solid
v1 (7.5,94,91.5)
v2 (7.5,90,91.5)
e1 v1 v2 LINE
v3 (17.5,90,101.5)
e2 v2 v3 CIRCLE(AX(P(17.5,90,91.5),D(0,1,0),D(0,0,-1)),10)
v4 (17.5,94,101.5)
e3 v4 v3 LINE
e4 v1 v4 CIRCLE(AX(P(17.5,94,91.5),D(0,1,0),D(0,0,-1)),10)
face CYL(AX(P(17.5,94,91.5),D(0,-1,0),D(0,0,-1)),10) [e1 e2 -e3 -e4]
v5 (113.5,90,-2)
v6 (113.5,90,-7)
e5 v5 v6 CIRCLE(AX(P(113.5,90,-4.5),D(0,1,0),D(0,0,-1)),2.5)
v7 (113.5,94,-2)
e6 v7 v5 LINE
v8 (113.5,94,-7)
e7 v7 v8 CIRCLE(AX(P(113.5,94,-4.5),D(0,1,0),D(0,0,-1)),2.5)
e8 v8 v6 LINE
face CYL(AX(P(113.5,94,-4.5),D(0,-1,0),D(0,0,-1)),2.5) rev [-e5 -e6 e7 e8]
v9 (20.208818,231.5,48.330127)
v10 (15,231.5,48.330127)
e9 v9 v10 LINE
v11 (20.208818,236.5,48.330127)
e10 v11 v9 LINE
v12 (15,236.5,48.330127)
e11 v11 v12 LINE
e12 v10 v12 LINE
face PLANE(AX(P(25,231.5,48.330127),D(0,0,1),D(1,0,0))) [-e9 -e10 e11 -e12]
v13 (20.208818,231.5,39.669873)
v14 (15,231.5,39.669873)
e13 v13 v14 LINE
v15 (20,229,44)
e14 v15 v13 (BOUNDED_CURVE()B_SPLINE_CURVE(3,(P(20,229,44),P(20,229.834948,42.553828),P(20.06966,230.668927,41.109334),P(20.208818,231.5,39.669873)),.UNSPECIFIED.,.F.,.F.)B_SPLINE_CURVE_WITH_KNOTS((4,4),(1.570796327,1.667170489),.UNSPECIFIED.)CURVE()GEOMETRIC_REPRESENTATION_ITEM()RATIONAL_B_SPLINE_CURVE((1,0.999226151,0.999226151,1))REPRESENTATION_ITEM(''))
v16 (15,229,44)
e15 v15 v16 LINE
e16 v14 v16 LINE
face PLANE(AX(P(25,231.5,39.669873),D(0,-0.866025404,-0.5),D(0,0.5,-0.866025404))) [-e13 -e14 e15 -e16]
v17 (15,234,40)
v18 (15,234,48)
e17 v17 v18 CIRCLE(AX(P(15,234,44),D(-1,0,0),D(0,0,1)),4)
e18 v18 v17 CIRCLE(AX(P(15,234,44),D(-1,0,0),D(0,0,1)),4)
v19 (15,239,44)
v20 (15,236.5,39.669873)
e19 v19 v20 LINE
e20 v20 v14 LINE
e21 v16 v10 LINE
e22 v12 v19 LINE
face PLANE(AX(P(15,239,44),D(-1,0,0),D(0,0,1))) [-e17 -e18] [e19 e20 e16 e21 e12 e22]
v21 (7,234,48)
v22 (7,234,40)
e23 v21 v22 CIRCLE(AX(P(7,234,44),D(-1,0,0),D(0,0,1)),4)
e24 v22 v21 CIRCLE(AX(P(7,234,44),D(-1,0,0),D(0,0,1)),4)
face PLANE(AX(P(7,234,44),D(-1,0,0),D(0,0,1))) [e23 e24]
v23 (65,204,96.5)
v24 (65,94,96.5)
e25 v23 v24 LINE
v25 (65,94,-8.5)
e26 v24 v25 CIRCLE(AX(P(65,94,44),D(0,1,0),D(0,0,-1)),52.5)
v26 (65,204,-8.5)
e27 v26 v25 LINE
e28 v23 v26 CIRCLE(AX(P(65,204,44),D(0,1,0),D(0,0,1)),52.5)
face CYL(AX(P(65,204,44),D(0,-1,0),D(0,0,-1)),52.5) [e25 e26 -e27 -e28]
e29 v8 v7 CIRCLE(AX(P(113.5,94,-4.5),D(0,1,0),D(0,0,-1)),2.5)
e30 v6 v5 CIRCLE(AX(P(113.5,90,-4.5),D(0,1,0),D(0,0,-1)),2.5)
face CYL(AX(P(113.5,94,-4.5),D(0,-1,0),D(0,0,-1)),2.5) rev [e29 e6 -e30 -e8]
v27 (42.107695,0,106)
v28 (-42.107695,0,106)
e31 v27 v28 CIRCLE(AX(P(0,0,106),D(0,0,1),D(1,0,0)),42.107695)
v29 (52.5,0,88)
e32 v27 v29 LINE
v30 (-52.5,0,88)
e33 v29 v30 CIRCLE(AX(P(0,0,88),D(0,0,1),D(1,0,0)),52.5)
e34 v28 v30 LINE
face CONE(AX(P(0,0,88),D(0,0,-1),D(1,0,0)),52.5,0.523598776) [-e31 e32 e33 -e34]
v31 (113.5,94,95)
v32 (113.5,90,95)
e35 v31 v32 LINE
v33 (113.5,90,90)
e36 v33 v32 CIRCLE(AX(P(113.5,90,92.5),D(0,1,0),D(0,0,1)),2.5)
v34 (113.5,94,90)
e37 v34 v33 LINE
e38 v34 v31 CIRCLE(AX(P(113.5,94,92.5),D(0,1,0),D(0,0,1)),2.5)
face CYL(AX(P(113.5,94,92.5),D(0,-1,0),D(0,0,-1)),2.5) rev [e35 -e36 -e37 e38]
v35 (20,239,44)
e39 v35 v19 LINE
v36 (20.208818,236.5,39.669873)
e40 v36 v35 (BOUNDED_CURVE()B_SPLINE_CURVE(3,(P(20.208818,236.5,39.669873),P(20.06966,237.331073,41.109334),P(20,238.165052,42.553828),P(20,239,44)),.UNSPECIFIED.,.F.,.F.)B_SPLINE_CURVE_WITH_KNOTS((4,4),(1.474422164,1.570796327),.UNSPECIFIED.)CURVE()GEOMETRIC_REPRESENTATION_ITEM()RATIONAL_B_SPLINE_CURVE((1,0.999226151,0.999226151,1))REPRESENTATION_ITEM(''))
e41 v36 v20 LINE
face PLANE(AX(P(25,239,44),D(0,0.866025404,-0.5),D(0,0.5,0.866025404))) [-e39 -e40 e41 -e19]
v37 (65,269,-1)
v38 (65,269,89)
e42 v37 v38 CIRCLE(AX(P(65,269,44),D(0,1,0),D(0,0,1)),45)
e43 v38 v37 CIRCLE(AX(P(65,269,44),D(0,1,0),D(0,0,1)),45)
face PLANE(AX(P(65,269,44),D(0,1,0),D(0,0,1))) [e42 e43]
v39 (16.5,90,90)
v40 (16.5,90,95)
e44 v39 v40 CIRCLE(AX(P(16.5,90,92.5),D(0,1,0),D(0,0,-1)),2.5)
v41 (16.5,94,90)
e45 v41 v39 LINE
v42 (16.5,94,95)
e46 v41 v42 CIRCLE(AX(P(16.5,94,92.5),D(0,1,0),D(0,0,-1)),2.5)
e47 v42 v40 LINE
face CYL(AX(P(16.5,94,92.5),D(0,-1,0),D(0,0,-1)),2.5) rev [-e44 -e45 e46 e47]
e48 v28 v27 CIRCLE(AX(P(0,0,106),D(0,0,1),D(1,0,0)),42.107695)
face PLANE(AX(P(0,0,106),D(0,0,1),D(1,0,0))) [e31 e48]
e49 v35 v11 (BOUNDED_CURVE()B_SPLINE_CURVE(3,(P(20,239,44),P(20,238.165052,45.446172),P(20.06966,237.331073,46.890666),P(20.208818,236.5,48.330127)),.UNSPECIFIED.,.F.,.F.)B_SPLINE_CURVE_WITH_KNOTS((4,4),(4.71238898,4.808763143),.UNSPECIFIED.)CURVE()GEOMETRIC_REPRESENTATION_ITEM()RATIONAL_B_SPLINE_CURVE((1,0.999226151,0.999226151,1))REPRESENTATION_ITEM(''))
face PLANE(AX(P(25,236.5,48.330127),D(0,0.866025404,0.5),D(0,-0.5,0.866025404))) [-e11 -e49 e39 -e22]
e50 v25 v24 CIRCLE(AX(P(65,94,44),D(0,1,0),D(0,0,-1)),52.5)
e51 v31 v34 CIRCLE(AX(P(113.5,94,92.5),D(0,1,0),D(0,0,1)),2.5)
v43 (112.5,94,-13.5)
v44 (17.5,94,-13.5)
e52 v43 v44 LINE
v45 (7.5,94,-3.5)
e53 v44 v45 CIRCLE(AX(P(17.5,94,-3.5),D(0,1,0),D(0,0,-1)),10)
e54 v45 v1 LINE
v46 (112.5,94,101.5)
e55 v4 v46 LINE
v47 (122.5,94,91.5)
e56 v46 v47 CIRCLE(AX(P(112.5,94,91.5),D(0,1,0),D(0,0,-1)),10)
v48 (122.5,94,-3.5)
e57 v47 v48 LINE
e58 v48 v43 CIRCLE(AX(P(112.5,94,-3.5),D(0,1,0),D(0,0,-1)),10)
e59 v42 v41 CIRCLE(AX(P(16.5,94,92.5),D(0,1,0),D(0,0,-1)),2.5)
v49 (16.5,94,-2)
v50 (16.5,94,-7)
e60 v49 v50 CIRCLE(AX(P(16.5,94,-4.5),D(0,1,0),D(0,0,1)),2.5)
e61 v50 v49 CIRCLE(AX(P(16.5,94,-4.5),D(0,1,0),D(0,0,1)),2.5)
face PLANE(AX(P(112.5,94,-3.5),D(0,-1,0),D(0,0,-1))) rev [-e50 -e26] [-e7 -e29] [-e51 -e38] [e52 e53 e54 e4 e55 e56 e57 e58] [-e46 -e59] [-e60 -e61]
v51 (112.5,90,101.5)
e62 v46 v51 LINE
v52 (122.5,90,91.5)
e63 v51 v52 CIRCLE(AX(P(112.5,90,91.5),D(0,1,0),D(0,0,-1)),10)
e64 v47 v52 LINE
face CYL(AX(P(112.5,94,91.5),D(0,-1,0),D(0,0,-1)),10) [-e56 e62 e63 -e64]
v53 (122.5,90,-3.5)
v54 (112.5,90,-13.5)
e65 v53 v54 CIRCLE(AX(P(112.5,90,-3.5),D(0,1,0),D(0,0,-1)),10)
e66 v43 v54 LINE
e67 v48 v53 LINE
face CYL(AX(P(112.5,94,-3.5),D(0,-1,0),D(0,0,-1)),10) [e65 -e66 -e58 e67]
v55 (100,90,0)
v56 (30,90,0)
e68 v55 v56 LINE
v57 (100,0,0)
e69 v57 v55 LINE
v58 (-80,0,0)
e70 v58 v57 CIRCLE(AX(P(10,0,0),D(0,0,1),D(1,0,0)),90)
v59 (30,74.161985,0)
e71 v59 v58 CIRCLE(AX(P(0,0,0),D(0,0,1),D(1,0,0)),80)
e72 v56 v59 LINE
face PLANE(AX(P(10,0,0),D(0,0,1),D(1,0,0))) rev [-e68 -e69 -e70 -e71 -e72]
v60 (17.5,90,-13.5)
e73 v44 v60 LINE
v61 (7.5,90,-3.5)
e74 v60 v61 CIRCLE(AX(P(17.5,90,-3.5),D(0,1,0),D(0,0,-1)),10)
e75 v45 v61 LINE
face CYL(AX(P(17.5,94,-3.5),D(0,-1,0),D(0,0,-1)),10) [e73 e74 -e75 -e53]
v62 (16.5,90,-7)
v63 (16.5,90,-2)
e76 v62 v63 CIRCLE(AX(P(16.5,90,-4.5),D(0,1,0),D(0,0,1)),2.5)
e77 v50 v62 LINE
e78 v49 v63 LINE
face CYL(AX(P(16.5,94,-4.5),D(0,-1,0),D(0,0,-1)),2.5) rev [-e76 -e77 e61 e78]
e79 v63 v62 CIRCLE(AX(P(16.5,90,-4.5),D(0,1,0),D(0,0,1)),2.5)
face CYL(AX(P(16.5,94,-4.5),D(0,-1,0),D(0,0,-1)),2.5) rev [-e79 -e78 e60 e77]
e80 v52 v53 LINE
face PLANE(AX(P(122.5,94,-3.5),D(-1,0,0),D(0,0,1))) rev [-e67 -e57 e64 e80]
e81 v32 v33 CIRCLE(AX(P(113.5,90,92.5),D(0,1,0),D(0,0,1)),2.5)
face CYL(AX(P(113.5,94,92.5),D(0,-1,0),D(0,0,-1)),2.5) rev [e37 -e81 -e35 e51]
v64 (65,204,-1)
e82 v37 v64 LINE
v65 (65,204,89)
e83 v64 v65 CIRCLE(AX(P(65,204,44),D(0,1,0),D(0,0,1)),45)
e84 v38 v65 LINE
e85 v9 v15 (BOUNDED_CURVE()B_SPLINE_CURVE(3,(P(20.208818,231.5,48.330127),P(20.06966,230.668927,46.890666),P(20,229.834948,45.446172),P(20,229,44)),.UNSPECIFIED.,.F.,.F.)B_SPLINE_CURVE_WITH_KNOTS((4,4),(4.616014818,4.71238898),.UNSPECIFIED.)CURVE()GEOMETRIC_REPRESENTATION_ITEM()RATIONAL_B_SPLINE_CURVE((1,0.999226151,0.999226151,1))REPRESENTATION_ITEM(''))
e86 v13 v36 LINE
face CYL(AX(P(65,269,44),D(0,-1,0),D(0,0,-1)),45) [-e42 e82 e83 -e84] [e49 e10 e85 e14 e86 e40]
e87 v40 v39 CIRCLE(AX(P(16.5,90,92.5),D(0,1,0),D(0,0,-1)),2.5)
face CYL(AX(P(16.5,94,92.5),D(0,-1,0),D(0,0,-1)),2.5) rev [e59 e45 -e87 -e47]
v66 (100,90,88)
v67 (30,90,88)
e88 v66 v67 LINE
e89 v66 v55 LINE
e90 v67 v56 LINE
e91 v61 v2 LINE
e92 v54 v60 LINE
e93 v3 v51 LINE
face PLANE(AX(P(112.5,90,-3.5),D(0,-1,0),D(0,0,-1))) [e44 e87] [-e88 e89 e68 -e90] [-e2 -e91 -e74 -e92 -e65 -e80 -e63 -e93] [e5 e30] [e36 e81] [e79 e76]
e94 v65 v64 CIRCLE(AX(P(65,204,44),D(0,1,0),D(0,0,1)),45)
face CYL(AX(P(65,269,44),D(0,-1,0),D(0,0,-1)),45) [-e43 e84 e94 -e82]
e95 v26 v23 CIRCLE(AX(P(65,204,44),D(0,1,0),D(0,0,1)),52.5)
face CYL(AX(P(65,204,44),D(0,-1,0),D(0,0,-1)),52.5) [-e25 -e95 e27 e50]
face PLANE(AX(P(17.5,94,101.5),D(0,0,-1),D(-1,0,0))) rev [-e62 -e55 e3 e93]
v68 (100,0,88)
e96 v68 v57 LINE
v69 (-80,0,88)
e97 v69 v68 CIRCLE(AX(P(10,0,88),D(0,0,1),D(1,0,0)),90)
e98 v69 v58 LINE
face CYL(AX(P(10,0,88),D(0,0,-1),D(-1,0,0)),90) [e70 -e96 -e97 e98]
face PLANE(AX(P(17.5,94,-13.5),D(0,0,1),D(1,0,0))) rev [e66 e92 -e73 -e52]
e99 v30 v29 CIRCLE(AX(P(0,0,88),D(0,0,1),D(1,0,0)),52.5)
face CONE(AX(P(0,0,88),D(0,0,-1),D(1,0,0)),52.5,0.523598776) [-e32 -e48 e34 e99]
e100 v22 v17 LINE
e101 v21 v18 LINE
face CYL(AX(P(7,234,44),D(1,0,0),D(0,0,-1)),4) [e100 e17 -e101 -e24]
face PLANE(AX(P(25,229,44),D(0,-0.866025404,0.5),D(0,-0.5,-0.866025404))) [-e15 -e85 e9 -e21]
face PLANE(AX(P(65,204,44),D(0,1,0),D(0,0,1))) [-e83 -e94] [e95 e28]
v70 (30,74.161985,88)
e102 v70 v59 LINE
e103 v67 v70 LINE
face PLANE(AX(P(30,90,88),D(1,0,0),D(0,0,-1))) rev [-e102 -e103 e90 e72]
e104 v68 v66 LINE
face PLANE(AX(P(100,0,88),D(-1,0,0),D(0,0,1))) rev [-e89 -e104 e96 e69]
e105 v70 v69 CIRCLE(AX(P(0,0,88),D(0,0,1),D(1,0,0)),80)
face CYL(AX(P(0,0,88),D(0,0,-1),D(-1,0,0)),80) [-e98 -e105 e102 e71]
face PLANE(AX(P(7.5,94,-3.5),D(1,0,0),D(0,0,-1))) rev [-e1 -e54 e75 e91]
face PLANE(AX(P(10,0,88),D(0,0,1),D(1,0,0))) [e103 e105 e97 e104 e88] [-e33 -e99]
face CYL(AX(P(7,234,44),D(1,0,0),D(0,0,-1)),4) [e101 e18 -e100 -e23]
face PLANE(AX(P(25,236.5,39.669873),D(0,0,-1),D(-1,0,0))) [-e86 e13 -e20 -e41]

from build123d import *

# Parameters (mm, degrees)
EXTRUDE_1_DEPTH      = 88
SKETCH_2_R           = 52.5
EXTRUDE_2_DEPTH      = 18
EXTRUDE_2_TAPER      = 30
SKETCH_3_R           = 2.5
EXTRUDE_3_DEPTH      = 4
SKETCH_4_R           = 52.5
EXTRUDE_4_DEPTH      = 110
SKETCH_5_R           = 45
EXTRUDE_5_DEPTH      = 65
EXTRUDE_6_DEPTH      = 5
EXTRUDE_6_DEPTH_BACK = 5
SKETCH_7_R           = 4
EXTRUDE_7_DEPTH      = 8


with BuildPart() as part:
    # 草图1 → 凸台-拉伸1 (new body)
    with BuildSketch(Plane.XY):
        with BuildLine():
            Line((100, 0), (100, 90))
            Line((100, 90), (30, 90))
            Line((30, 90), (30, 74.161984871))
            ThreePointArc((30, 74.161984871), (-44.72135955, 66.332495807), (-80, 0))
            ThreePointArc((-80, 0), (10, -90), (100, 0))
        make_face()
    extrude(amount=EXTRUDE_1_DEPTH)

    # 草图2 → 凸台-拉伸2 (add)
    with BuildSketch(Plane.XY.offset(88)):
        Circle(SKETCH_2_R)
    extrude(amount=EXTRUDE_2_DEPTH, taper=EXTRUDE_2_TAPER)

    # 草图3 → 凸台-拉伸3 (add)
    with BuildSketch(Plane(origin=(0, 90, 0), x_dir=(1, 0, 0), z_dir=(0, 1, 0))):
        with BuildLine():
            Line((17.5, 13.5), (112.5, 13.5))
            ThreePointArc((112.5, 13.5), (119.571067812, 10.571067812), (122.5, 3.5))
            Line((122.5, 3.5), (122.5, -91.5))
            ThreePointArc((122.5, -91.5), (119.571067812, -98.571067812), (112.5, -101.5))
            Line((112.5, -101.5), (17.5, -101.5))
            ThreePointArc((17.5, -101.5), (10.428932188, -98.571067812), (7.5, -91.5))
            Line((7.5, -91.5), (7.5, 3.5))
            ThreePointArc((7.5, 3.5), (10.428932188, 10.571067812), (17.5, 13.5))
        make_face()
        with Locations(Location((16.5, 4.5, 0), (0, 0, 270))):
            Circle(SKETCH_3_R, mode=Mode.SUBTRACT)
        with Locations(Location((16.5, -92.5, 0), (0, 0, 90))):
            Circle(SKETCH_3_R, mode=Mode.SUBTRACT)
        with Locations(Location((113.5, -92.5, 0), (0, 0, 270))):
            Circle(SKETCH_3_R, mode=Mode.SUBTRACT)
        with Locations(Location((113.5, 4.5, 0), (0, 0, 90))):
            Circle(SKETCH_3_R, mode=Mode.SUBTRACT)
    extrude(amount=EXTRUDE_3_DEPTH)

    # 草图4 → 凸台-拉伸4 (add)
    with BuildSketch(Plane(origin=(0, 94, 0), x_dir=(1, 0, 0), z_dir=(0, 1, 0))):
        with Locations(Location((65, -44, 0), (0, 0, 90))):
            Circle(SKETCH_4_R)
    extrude(amount=EXTRUDE_4_DEPTH)

    # 草图5 → 凸台-拉伸5 (add)
    with BuildSketch(Plane(origin=(0, 204, 0), x_dir=(1, 0, 0), z_dir=(0, 1, 0))):
        with Locations(Location((65, -44, 0), (0, 0, 270))):
            Circle(SKETCH_5_R)
    extrude(amount=EXTRUDE_5_DEPTH)



with BuildPart() as body_2:
    # 草图6 → 凸台-拉伸6 (new, two sides: drawn at the far end of the back side and taken through both)
    with BuildSketch(Plane.ZY.offset(-20).offset(-EXTRUDE_6_DEPTH_BACK)):
        Polygon((44, 239), (39.669872981, 236.5), (39.669872981, 231.5), (44, 229), (48.330127019, 231.5), (48.330127019, 236.5), align=None)
    extrude(amount=EXTRUDE_6_DEPTH + EXTRUDE_6_DEPTH_BACK)


with BuildPart() as part_1:
    add(part.part)

    add(body_2.part)  # 凸台-拉伸7 merges body 2
    # 草图7 → 凸台-拉伸7 (add)
    with BuildSketch(Plane.ZY.offset(-15)):
        with Locations((44, 234)):
            Circle(SKETCH_7_R)
    extrude(amount=EXTRUDE_7_DEPTH)


solid = part_1.part
